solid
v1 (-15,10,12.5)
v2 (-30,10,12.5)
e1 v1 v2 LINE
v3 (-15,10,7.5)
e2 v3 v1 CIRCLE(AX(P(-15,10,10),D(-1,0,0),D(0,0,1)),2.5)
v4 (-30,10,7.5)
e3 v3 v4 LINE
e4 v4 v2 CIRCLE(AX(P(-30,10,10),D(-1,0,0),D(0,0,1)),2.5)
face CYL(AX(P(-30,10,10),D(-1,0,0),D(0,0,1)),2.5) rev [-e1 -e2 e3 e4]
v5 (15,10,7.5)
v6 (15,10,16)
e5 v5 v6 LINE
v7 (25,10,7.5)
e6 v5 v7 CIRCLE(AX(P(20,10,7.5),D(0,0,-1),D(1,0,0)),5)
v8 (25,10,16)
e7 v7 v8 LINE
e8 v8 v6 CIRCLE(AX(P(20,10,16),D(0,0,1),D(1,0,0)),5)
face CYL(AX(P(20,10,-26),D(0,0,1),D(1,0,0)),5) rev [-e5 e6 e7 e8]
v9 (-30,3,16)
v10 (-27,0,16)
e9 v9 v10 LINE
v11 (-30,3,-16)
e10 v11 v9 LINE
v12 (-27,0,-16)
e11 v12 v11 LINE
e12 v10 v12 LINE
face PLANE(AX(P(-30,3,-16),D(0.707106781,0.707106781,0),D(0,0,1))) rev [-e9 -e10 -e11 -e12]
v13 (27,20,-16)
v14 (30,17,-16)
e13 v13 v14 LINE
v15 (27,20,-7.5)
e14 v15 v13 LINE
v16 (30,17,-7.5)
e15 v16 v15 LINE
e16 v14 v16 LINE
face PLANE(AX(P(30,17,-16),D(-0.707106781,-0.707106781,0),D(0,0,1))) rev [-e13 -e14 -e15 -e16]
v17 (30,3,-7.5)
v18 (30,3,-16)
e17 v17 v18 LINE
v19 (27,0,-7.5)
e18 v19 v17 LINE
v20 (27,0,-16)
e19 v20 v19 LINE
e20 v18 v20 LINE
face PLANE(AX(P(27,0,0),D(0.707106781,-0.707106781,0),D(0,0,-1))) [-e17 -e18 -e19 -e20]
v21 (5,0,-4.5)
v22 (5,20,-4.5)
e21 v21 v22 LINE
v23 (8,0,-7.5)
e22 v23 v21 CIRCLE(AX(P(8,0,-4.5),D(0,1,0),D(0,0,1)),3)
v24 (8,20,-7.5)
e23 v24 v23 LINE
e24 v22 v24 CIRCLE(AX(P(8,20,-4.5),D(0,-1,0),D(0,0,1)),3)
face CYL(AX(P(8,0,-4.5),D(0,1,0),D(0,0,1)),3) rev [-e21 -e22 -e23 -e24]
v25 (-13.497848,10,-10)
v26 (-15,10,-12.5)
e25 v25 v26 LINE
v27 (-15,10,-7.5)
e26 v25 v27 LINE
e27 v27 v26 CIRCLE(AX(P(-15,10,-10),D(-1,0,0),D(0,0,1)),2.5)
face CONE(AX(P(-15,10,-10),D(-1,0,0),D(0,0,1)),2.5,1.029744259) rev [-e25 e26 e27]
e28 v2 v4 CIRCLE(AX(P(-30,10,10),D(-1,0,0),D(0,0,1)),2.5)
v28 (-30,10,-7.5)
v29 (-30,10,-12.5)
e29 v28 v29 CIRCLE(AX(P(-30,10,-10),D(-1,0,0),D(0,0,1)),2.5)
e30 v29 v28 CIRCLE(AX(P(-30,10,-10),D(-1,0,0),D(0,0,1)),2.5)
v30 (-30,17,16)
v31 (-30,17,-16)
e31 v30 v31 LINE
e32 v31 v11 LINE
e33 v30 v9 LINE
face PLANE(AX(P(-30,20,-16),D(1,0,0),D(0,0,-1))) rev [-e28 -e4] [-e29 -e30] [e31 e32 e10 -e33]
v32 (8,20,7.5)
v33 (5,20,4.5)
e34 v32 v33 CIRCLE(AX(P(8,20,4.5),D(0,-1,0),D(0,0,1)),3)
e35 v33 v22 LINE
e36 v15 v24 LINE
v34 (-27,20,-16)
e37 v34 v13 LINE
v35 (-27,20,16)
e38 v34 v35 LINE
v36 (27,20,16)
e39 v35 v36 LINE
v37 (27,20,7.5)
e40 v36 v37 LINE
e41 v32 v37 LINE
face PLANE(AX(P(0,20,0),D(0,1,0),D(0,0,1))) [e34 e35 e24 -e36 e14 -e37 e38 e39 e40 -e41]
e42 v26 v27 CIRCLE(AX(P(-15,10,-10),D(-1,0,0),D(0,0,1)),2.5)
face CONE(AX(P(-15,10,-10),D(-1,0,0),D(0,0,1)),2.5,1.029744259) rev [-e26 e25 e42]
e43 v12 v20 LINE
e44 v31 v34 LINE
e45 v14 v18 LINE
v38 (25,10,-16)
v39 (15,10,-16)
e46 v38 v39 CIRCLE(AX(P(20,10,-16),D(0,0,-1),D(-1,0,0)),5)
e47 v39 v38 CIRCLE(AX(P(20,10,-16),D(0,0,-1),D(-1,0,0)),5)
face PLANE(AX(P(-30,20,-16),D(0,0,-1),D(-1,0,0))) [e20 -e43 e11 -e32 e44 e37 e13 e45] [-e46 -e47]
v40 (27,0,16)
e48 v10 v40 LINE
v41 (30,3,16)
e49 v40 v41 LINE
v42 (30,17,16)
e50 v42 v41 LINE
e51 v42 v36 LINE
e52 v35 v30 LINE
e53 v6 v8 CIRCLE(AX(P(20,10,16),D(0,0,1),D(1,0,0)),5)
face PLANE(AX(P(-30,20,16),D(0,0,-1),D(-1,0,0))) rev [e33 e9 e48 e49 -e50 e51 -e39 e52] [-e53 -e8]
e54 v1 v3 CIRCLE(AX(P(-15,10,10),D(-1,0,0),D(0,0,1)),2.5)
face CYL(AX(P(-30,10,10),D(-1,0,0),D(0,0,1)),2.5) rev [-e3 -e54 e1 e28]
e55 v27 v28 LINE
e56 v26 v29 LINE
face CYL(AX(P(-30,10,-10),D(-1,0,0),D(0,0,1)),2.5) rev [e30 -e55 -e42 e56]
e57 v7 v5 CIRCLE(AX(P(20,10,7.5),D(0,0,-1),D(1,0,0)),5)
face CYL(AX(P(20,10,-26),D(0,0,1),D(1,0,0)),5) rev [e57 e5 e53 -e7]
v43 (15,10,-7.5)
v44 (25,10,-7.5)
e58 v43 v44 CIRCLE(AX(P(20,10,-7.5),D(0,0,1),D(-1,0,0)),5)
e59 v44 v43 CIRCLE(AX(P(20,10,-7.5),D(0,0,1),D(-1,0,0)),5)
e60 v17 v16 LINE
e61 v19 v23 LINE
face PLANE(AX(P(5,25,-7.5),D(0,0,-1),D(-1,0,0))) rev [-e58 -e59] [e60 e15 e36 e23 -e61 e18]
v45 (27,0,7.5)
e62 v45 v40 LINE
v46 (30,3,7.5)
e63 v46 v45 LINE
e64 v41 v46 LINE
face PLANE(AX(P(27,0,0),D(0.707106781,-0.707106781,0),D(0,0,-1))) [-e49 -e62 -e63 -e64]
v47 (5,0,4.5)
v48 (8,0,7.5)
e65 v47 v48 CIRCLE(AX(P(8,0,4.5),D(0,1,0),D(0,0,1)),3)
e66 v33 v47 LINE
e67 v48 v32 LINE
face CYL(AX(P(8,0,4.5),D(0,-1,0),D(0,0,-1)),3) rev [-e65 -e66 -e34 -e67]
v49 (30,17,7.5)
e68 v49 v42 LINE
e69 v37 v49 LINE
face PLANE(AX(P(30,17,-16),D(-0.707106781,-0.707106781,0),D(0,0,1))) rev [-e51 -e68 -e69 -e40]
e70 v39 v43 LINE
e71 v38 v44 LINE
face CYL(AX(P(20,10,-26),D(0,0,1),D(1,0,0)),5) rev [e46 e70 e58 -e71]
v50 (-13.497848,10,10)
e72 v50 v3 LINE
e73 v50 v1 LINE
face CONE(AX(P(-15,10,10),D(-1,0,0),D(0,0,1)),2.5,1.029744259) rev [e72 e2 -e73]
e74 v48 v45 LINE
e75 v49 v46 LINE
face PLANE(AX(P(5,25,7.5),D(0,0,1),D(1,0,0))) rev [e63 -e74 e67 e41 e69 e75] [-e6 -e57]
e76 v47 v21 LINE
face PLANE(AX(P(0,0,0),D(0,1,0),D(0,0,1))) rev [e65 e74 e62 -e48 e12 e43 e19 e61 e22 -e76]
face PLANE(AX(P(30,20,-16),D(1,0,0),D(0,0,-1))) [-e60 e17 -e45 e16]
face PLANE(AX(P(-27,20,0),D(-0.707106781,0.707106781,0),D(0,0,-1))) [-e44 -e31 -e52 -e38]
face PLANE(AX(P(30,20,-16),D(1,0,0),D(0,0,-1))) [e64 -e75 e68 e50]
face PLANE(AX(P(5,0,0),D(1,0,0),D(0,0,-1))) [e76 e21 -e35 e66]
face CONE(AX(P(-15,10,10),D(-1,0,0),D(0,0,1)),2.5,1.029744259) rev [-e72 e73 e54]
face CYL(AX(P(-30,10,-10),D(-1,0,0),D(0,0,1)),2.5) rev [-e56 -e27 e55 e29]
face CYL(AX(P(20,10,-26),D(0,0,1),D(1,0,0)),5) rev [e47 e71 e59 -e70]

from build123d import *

# Parameters (mm, degrees)
SKETCH1_W             = 60
SKETCH1_H             = 32
BOSS_EXTRUDE1_DEPTH   = 20
SKETCH2_R             = 5
CUT_EXTRUDE1_DEPTH    = 42
CHAMFER1_SIZE         = 3
M6_TAPPED_HOLE1_D     = 5
M6_TAPPED_HOLE1_DEPTH = 15
M6_TAPPED_HOLE1_TIP   = 1.502151548
SKETCH6_W             = 15
SKETCH6_H             = 30
CUT_EXTRUDE2_DEPTH    = 25
FILLET1_R             = 3


with BuildPart() as part:
    # Sketch1 → Boss-Extrude1 (new body)
    with BuildSketch(Plane(origin=(0, 0, 0), x_dir=(1, 0, 0), z_dir=(0, 1, 0))):
        Rectangle(SKETCH1_W, SKETCH1_H)
    extrude(amount=BOSS_EXTRUDE1_DEPTH)

    # Sketch2 → Cut-Extrude1 (cut)
    with BuildSketch(Plane.XY.offset(16)):
        with Locations((20, 10)):
            Circle(SKETCH2_R)
    extrude(amount=-CUT_EXTRUDE1_DEPTH, mode=Mode.SUBTRACT)

    # Chamfer1
    chamfer1_edges = [part.edges().sort_by_distance(p)[0] for p in [
        (30, 20, 0),
        (-30, 20, 0),
        (30, 0, 0),
        (-30, 0, 0),
    ]]
    chamfer(chamfer1_edges, length=CHAMFER1_SIZE)

    # M6 Tapped Hole1
    with Locations(Plane.ZY.offset(30)):
        with Locations((-10, 10), (10, 10)):
            Hole(M6_TAPPED_HOLE1_D / 2, depth=M6_TAPPED_HOLE1_DEPTH)
            with Locations((0, 0, -(M6_TAPPED_HOLE1_DEPTH + M6_TAPPED_HOLE1_TIP / 2))):  # 118° drill point
                Cone(0, M6_TAPPED_HOLE1_D / 2, M6_TAPPED_HOLE1_TIP, mode=Mode.SUBTRACT)

    # Sketch6 → Cut-Extrude2 (cut)
    with BuildSketch(Plane(origin=(30, 0, 0), x_dir=(0, 0, -1), z_dir=(1, 0, 0))):
        with Locations((0, 10)):
            Rectangle(SKETCH6_W, SKETCH6_H)
    extrude(amount=-CUT_EXTRUDE2_DEPTH, mode=Mode.SUBTRACT)

    # Fillet1
    fillet1_edges = [part.edges().sort_by_distance(p)[0] for p in [
        (5, 10, -7.5),
        (5, 10, 7.5),
    ]]
    fillet(fillet1_edges, radius=FILLET1_R)


solid = part.part
